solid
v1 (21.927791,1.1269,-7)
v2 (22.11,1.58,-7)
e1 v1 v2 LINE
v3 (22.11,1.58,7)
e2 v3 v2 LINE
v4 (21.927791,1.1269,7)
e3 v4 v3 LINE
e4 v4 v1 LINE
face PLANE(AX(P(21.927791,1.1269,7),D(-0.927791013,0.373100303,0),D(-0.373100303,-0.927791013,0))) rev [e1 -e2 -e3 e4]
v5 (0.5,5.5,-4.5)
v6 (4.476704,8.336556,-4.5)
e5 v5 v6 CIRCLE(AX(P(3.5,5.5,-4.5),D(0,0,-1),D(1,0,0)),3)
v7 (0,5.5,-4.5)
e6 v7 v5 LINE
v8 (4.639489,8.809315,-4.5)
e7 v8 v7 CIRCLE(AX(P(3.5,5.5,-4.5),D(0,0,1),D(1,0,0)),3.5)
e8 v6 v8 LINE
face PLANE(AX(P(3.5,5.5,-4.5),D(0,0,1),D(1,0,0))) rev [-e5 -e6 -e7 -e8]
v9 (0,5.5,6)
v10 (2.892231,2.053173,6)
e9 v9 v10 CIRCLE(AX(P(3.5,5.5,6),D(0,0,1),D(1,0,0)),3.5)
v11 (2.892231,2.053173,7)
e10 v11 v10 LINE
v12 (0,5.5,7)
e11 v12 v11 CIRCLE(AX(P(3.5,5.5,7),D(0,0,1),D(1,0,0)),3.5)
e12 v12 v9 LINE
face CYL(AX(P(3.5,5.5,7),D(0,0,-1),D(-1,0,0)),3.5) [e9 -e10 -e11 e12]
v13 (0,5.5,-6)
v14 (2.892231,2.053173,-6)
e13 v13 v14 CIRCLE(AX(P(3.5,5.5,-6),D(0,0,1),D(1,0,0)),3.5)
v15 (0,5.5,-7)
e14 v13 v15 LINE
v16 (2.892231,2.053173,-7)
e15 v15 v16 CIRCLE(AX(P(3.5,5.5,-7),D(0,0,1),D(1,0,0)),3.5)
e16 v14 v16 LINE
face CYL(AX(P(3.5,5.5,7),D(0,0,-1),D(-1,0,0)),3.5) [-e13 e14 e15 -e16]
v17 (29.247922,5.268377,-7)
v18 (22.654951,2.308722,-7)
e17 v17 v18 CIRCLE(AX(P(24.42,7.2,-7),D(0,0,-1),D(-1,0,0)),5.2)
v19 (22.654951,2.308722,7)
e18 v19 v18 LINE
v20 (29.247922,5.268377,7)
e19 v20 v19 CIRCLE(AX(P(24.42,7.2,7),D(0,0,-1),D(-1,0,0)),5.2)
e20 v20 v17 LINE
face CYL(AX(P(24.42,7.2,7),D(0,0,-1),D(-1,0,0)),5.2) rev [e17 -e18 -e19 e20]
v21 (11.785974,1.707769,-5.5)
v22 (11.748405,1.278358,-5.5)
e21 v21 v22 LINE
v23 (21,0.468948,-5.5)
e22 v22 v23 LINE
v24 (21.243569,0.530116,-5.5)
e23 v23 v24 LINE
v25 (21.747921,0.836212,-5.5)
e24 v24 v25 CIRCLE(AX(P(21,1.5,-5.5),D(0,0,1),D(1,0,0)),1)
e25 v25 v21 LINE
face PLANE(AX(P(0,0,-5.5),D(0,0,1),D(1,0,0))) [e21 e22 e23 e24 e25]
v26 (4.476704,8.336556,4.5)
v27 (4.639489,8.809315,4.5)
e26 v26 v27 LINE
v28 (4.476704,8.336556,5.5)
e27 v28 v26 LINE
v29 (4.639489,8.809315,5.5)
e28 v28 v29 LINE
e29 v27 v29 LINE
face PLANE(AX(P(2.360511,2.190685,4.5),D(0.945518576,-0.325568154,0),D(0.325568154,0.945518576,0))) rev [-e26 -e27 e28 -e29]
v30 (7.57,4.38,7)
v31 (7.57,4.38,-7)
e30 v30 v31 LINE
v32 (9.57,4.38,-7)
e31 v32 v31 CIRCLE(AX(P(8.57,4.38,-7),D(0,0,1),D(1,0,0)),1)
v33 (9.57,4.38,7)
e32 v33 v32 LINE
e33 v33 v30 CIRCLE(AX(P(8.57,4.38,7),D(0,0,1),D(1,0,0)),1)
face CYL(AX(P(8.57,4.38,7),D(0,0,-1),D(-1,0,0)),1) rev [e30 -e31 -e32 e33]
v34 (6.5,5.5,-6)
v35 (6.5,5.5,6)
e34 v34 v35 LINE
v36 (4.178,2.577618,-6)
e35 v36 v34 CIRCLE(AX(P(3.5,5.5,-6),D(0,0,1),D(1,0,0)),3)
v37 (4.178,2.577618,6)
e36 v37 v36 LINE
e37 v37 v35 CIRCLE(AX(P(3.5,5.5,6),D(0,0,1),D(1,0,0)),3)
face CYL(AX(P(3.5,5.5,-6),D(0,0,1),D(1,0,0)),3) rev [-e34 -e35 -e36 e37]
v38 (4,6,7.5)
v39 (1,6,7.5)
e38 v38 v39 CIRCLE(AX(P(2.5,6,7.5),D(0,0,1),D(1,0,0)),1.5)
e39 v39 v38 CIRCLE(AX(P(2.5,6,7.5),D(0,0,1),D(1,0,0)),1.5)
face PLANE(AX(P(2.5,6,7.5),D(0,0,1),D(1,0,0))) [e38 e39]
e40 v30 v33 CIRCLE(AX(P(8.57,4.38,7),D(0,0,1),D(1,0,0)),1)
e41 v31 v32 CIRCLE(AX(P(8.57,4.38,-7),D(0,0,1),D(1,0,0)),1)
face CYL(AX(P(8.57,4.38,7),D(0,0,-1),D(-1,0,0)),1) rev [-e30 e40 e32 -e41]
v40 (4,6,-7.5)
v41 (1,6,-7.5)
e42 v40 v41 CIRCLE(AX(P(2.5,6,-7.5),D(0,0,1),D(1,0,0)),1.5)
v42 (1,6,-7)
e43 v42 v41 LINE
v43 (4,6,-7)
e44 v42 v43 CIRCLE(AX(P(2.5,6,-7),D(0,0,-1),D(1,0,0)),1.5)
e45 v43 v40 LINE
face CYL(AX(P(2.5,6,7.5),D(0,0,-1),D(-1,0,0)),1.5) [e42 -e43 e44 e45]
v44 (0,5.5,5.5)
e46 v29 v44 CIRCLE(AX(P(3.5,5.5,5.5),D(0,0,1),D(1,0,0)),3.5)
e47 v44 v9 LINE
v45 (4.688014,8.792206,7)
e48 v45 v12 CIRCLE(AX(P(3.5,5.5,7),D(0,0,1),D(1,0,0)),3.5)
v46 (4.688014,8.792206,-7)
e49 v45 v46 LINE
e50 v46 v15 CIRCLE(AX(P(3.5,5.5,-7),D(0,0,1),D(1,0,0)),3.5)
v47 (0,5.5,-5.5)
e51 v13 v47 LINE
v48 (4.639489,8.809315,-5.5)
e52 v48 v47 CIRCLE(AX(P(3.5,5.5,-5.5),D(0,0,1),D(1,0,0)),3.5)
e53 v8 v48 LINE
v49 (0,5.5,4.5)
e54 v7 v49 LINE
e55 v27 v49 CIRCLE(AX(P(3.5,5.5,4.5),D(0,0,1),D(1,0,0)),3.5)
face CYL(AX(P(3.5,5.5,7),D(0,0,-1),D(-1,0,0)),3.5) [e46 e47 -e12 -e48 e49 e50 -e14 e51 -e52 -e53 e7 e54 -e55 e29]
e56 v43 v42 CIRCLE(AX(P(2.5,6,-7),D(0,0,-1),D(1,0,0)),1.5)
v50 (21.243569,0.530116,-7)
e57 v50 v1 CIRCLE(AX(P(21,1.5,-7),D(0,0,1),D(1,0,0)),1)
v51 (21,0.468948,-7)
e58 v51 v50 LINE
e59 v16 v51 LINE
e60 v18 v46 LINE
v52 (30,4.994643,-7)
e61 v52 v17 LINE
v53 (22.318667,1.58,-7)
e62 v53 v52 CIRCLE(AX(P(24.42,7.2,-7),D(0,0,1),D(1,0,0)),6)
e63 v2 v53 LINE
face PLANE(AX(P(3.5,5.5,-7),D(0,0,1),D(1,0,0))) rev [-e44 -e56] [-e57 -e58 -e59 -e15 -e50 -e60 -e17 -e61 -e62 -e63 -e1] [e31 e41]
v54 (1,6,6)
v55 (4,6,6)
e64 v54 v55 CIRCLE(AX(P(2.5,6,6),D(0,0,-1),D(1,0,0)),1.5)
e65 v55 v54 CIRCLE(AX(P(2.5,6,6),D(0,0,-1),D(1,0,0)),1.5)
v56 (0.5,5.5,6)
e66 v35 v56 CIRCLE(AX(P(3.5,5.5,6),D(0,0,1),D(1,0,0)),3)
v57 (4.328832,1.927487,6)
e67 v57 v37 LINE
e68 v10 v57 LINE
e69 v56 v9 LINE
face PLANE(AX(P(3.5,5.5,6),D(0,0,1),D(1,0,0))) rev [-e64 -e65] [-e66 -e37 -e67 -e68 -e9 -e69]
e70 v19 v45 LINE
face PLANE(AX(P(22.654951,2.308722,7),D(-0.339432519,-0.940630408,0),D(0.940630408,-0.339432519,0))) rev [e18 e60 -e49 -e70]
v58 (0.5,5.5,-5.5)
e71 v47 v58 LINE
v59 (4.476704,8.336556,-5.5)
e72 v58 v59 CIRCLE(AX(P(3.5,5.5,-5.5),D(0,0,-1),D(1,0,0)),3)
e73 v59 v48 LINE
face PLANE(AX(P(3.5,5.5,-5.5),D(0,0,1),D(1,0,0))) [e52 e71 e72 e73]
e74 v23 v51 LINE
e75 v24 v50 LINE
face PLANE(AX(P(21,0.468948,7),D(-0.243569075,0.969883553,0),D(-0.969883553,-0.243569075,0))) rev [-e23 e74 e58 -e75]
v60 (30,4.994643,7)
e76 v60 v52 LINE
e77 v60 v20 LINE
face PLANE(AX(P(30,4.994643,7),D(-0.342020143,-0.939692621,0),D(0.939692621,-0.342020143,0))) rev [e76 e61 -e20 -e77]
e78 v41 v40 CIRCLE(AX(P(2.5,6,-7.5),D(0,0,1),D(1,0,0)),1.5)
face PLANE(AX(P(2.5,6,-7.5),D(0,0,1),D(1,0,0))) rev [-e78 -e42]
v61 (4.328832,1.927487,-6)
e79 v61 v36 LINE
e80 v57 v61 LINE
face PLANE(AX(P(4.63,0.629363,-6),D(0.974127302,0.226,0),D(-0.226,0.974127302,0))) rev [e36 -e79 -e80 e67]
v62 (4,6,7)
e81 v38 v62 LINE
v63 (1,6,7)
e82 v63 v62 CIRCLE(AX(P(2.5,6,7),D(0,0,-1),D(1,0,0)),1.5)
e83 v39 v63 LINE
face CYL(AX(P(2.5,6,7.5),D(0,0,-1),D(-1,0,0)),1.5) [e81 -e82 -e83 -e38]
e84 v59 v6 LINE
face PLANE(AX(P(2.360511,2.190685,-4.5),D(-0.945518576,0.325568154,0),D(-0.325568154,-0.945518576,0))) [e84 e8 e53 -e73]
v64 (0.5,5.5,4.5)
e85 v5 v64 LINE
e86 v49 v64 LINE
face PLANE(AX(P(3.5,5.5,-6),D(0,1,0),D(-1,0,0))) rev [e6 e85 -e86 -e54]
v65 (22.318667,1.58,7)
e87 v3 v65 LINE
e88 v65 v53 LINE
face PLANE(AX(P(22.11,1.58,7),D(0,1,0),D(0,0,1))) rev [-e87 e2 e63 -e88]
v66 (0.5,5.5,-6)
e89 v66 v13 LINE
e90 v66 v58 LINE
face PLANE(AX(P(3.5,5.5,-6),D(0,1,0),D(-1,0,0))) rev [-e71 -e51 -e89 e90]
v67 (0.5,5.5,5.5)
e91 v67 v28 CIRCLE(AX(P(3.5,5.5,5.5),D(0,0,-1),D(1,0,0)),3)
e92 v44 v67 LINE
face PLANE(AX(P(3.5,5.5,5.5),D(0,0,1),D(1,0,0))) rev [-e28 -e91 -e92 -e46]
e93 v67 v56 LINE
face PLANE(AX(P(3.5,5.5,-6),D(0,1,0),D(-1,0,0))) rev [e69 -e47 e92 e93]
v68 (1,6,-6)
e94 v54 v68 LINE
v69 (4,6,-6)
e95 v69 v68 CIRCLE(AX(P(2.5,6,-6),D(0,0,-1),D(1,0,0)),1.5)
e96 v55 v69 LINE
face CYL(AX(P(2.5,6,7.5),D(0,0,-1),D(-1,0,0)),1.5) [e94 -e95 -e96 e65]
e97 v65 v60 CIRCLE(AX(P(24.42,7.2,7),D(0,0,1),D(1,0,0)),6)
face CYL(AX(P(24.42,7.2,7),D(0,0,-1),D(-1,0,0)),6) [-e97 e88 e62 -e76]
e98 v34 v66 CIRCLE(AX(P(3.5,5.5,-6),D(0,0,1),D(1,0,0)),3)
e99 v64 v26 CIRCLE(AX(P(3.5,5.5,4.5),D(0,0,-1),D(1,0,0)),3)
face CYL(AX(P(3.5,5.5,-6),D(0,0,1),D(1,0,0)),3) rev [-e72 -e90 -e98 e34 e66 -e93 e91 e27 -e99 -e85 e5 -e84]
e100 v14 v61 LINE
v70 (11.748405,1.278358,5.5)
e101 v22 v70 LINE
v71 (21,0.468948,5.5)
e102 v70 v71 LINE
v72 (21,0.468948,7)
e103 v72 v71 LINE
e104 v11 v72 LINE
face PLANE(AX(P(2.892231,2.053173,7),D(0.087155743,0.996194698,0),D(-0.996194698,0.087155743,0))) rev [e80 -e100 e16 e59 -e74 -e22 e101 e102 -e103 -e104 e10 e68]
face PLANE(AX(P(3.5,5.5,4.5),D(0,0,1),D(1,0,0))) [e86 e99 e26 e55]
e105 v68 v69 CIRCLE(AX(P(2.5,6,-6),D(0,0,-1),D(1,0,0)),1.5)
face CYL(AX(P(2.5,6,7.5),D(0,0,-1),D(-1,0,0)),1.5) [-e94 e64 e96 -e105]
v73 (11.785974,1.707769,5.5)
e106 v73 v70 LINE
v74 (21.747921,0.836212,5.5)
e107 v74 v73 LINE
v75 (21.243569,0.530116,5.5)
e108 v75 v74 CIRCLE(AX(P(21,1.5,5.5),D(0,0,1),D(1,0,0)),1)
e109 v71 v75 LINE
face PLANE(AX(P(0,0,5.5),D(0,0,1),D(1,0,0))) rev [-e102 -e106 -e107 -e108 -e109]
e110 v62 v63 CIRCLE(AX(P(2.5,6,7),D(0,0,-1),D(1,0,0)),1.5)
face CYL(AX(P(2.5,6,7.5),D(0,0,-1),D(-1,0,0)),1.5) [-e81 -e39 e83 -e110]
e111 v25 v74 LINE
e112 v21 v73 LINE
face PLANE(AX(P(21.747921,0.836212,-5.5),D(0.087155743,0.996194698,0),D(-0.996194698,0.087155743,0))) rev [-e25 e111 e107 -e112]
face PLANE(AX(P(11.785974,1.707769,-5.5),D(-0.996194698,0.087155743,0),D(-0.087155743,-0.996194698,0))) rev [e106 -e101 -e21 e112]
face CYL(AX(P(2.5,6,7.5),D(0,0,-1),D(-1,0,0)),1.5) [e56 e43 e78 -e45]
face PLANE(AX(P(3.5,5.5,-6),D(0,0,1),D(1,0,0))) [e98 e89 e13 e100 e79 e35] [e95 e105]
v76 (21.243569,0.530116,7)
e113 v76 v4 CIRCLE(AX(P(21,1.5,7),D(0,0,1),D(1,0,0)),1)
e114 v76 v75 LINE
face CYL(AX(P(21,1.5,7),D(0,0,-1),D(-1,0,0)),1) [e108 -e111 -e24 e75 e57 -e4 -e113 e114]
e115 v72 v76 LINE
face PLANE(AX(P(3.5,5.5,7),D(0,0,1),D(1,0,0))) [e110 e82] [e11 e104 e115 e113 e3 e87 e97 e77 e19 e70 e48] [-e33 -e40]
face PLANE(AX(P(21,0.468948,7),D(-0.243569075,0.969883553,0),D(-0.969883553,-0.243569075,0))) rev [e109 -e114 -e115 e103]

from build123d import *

# Parameters (mm, degrees)
EXTRUDE_1_DEPTH          = 7
EXTRUDE_1_DEPTH_BACK     = 7
SKETCH_1_R               = 1
CUT_EXTRUDE_1_DEPTH      = 6
CUT_EXTRUDE_1_DEPTH_BACK = 6
CUT_EXTRUDE_2_DEPTH      = 6
CUT_EXTRUDE_2_DEPTH_BACK = 6
SKETCH_3_R               = 3
CUT_EXTRUDE_START        = -1
CUT_EXTRUDE_3_DEPTH      = 1
CUT_EXTRUDE_4_DEPTH      = 1
EXTRUDE_2_DEPTH          = 7.5
EXTRUDE_2_DEPTH_BACK     = 7.5
SKETCH_6_R               = 1.5
CUT_EXTRUDE_5_DEPTH      = 5.5
CUT_EXTRUDE_5_DEPTH_BACK = 5.5


with BuildPart() as part:
    # 草图1 → 凸台-拉伸1 (new, two sides: drawn at the far end of the back side and taken through both)
    with BuildSketch(Plane.XY.offset(-EXTRUDE_1_DEPTH_BACK)):
        with BuildLine():
            Line((2.892231378, 2.053172864), (21, 0.468948388))
            Line((21, 0.468948388), (21.243569075, 0.530116447))
            ThreePointArc((21.243569075, 0.530116447), (21.657311704, 0.746381181), (21.927791013, 1.126899697))
            Line((21.927791013, 1.126899697), (22.11, 1.58))
            Line((22.11, 1.58), (22.31866709, 1.58))
            ThreePointArc((22.31866709, 1.58), (26.857258232, 1.7173207), (30, 4.994642886))
            Line((30, 4.994642886), (29.24792212, 5.268376848))
            ThreePointArc((29.24792212, 5.268376848), (26.549597889, 2.45607622), (22.654950899, 2.308721878))
            Line((22.654950899, 2.308721878), (4.688013818, 8.792206429))
            ThreePointArc((4.688013818, 8.792206429), (0.118016194, 6.401213367), (2.892231378, 2.053172864))
        make_face()
        with Locations((8.57, 4.38)):
            Circle(SKETCH_1_R, mode=Mode.SUBTRACT)
    extrude(amount=EXTRUDE_1_DEPTH + EXTRUDE_1_DEPTH_BACK)

    # 草图2 → 切除-拉伸1 (cut, two sides: drawn at the far end of the back side and taken through both)
    with BuildSketch(Plane.XY.offset(-CUT_EXTRUDE_1_DEPTH_BACK)):
        with BuildLine():
            Line((4.63, 0.629363491), (3.5, 5.5))
            Line((3.5, 5.5), (-1.5, 5.5))
            ThreePointArc((-1.5, 5.5), (0.389533797, 1.585284174), (4.63, 0.629363491))
        make_face()
    extrude(amount=CUT_EXTRUDE_1_DEPTH + CUT_EXTRUDE_1_DEPTH_BACK, mode=Mode.SUBTRACT)

    # 草图3 → 切除-拉伸2 (cut, two sides: drawn at the far end of the back side and taken through both)
    with BuildSketch(Plane.XY.offset(-CUT_EXTRUDE_2_DEPTH_BACK)):
        with Locations((3.5, 5.5)):
            Circle(SKETCH_3_R)
    extrude(amount=CUT_EXTRUDE_2_DEPTH + CUT_EXTRUDE_2_DEPTH_BACK, mode=Mode.SUBTRACT)

    # 草图4 → 切除-拉伸3 (cut)
    with BuildSketch(Plane.XY.offset(5.5).offset(CUT_EXTRUDE_START)):
        with BuildLine():
            Line((2.360511459, 2.190684985), (4.639488541, 8.809315015))
            ThreePointArc((4.639488541, 8.809315015), (0.190684985, 6.639488541), (2.360511459, 2.190684985))
        make_face()
    extrude(amount=CUT_EXTRUDE_3_DEPTH, mode=Mode.SUBTRACT)

    # 草图5 → 切除-拉伸4 (cut)
    with BuildSketch(Plane.XY.offset(-5.5)):
        with BuildLine():
            Line((2.360511459, 2.190684985), (4.639488541, 8.809315015))
            ThreePointArc((4.639488541, 8.809315015), (0.190684985, 6.639488541), (2.360511459, 2.190684985))
        make_face()
    extrude(amount=CUT_EXTRUDE_4_DEPTH, mode=Mode.SUBTRACT)

    # 草图6 → 凸台-拉伸2 (add, two sides: drawn at the far end of the back side and taken through both)
    with BuildSketch(Plane.XY.offset(-EXTRUDE_2_DEPTH_BACK)):
        with Locations((2.5, 6)):
            Circle(SKETCH_6_R)
    extrude(amount=EXTRUDE_2_DEPTH + EXTRUDE_2_DEPTH_BACK)

    # 草图7 → 切除-拉伸5 (cut, two sides: drawn at the far end of the back side and taken through both)
    with BuildSketch(Plane.XY.offset(-CUT_EXTRUDE_5_DEPTH_BACK)):
        Polygon((11.724964743, 1.0104331), (21.686911724, 0.138875672), (21.747920744, 0.836211961), (11.785973763, 1.707769388), align=None)
    extrude(amount=CUT_EXTRUDE_5_DEPTH + CUT_EXTRUDE_5_DEPTH_BACK, mode=Mode.SUBTRACT)


solid = part.part
